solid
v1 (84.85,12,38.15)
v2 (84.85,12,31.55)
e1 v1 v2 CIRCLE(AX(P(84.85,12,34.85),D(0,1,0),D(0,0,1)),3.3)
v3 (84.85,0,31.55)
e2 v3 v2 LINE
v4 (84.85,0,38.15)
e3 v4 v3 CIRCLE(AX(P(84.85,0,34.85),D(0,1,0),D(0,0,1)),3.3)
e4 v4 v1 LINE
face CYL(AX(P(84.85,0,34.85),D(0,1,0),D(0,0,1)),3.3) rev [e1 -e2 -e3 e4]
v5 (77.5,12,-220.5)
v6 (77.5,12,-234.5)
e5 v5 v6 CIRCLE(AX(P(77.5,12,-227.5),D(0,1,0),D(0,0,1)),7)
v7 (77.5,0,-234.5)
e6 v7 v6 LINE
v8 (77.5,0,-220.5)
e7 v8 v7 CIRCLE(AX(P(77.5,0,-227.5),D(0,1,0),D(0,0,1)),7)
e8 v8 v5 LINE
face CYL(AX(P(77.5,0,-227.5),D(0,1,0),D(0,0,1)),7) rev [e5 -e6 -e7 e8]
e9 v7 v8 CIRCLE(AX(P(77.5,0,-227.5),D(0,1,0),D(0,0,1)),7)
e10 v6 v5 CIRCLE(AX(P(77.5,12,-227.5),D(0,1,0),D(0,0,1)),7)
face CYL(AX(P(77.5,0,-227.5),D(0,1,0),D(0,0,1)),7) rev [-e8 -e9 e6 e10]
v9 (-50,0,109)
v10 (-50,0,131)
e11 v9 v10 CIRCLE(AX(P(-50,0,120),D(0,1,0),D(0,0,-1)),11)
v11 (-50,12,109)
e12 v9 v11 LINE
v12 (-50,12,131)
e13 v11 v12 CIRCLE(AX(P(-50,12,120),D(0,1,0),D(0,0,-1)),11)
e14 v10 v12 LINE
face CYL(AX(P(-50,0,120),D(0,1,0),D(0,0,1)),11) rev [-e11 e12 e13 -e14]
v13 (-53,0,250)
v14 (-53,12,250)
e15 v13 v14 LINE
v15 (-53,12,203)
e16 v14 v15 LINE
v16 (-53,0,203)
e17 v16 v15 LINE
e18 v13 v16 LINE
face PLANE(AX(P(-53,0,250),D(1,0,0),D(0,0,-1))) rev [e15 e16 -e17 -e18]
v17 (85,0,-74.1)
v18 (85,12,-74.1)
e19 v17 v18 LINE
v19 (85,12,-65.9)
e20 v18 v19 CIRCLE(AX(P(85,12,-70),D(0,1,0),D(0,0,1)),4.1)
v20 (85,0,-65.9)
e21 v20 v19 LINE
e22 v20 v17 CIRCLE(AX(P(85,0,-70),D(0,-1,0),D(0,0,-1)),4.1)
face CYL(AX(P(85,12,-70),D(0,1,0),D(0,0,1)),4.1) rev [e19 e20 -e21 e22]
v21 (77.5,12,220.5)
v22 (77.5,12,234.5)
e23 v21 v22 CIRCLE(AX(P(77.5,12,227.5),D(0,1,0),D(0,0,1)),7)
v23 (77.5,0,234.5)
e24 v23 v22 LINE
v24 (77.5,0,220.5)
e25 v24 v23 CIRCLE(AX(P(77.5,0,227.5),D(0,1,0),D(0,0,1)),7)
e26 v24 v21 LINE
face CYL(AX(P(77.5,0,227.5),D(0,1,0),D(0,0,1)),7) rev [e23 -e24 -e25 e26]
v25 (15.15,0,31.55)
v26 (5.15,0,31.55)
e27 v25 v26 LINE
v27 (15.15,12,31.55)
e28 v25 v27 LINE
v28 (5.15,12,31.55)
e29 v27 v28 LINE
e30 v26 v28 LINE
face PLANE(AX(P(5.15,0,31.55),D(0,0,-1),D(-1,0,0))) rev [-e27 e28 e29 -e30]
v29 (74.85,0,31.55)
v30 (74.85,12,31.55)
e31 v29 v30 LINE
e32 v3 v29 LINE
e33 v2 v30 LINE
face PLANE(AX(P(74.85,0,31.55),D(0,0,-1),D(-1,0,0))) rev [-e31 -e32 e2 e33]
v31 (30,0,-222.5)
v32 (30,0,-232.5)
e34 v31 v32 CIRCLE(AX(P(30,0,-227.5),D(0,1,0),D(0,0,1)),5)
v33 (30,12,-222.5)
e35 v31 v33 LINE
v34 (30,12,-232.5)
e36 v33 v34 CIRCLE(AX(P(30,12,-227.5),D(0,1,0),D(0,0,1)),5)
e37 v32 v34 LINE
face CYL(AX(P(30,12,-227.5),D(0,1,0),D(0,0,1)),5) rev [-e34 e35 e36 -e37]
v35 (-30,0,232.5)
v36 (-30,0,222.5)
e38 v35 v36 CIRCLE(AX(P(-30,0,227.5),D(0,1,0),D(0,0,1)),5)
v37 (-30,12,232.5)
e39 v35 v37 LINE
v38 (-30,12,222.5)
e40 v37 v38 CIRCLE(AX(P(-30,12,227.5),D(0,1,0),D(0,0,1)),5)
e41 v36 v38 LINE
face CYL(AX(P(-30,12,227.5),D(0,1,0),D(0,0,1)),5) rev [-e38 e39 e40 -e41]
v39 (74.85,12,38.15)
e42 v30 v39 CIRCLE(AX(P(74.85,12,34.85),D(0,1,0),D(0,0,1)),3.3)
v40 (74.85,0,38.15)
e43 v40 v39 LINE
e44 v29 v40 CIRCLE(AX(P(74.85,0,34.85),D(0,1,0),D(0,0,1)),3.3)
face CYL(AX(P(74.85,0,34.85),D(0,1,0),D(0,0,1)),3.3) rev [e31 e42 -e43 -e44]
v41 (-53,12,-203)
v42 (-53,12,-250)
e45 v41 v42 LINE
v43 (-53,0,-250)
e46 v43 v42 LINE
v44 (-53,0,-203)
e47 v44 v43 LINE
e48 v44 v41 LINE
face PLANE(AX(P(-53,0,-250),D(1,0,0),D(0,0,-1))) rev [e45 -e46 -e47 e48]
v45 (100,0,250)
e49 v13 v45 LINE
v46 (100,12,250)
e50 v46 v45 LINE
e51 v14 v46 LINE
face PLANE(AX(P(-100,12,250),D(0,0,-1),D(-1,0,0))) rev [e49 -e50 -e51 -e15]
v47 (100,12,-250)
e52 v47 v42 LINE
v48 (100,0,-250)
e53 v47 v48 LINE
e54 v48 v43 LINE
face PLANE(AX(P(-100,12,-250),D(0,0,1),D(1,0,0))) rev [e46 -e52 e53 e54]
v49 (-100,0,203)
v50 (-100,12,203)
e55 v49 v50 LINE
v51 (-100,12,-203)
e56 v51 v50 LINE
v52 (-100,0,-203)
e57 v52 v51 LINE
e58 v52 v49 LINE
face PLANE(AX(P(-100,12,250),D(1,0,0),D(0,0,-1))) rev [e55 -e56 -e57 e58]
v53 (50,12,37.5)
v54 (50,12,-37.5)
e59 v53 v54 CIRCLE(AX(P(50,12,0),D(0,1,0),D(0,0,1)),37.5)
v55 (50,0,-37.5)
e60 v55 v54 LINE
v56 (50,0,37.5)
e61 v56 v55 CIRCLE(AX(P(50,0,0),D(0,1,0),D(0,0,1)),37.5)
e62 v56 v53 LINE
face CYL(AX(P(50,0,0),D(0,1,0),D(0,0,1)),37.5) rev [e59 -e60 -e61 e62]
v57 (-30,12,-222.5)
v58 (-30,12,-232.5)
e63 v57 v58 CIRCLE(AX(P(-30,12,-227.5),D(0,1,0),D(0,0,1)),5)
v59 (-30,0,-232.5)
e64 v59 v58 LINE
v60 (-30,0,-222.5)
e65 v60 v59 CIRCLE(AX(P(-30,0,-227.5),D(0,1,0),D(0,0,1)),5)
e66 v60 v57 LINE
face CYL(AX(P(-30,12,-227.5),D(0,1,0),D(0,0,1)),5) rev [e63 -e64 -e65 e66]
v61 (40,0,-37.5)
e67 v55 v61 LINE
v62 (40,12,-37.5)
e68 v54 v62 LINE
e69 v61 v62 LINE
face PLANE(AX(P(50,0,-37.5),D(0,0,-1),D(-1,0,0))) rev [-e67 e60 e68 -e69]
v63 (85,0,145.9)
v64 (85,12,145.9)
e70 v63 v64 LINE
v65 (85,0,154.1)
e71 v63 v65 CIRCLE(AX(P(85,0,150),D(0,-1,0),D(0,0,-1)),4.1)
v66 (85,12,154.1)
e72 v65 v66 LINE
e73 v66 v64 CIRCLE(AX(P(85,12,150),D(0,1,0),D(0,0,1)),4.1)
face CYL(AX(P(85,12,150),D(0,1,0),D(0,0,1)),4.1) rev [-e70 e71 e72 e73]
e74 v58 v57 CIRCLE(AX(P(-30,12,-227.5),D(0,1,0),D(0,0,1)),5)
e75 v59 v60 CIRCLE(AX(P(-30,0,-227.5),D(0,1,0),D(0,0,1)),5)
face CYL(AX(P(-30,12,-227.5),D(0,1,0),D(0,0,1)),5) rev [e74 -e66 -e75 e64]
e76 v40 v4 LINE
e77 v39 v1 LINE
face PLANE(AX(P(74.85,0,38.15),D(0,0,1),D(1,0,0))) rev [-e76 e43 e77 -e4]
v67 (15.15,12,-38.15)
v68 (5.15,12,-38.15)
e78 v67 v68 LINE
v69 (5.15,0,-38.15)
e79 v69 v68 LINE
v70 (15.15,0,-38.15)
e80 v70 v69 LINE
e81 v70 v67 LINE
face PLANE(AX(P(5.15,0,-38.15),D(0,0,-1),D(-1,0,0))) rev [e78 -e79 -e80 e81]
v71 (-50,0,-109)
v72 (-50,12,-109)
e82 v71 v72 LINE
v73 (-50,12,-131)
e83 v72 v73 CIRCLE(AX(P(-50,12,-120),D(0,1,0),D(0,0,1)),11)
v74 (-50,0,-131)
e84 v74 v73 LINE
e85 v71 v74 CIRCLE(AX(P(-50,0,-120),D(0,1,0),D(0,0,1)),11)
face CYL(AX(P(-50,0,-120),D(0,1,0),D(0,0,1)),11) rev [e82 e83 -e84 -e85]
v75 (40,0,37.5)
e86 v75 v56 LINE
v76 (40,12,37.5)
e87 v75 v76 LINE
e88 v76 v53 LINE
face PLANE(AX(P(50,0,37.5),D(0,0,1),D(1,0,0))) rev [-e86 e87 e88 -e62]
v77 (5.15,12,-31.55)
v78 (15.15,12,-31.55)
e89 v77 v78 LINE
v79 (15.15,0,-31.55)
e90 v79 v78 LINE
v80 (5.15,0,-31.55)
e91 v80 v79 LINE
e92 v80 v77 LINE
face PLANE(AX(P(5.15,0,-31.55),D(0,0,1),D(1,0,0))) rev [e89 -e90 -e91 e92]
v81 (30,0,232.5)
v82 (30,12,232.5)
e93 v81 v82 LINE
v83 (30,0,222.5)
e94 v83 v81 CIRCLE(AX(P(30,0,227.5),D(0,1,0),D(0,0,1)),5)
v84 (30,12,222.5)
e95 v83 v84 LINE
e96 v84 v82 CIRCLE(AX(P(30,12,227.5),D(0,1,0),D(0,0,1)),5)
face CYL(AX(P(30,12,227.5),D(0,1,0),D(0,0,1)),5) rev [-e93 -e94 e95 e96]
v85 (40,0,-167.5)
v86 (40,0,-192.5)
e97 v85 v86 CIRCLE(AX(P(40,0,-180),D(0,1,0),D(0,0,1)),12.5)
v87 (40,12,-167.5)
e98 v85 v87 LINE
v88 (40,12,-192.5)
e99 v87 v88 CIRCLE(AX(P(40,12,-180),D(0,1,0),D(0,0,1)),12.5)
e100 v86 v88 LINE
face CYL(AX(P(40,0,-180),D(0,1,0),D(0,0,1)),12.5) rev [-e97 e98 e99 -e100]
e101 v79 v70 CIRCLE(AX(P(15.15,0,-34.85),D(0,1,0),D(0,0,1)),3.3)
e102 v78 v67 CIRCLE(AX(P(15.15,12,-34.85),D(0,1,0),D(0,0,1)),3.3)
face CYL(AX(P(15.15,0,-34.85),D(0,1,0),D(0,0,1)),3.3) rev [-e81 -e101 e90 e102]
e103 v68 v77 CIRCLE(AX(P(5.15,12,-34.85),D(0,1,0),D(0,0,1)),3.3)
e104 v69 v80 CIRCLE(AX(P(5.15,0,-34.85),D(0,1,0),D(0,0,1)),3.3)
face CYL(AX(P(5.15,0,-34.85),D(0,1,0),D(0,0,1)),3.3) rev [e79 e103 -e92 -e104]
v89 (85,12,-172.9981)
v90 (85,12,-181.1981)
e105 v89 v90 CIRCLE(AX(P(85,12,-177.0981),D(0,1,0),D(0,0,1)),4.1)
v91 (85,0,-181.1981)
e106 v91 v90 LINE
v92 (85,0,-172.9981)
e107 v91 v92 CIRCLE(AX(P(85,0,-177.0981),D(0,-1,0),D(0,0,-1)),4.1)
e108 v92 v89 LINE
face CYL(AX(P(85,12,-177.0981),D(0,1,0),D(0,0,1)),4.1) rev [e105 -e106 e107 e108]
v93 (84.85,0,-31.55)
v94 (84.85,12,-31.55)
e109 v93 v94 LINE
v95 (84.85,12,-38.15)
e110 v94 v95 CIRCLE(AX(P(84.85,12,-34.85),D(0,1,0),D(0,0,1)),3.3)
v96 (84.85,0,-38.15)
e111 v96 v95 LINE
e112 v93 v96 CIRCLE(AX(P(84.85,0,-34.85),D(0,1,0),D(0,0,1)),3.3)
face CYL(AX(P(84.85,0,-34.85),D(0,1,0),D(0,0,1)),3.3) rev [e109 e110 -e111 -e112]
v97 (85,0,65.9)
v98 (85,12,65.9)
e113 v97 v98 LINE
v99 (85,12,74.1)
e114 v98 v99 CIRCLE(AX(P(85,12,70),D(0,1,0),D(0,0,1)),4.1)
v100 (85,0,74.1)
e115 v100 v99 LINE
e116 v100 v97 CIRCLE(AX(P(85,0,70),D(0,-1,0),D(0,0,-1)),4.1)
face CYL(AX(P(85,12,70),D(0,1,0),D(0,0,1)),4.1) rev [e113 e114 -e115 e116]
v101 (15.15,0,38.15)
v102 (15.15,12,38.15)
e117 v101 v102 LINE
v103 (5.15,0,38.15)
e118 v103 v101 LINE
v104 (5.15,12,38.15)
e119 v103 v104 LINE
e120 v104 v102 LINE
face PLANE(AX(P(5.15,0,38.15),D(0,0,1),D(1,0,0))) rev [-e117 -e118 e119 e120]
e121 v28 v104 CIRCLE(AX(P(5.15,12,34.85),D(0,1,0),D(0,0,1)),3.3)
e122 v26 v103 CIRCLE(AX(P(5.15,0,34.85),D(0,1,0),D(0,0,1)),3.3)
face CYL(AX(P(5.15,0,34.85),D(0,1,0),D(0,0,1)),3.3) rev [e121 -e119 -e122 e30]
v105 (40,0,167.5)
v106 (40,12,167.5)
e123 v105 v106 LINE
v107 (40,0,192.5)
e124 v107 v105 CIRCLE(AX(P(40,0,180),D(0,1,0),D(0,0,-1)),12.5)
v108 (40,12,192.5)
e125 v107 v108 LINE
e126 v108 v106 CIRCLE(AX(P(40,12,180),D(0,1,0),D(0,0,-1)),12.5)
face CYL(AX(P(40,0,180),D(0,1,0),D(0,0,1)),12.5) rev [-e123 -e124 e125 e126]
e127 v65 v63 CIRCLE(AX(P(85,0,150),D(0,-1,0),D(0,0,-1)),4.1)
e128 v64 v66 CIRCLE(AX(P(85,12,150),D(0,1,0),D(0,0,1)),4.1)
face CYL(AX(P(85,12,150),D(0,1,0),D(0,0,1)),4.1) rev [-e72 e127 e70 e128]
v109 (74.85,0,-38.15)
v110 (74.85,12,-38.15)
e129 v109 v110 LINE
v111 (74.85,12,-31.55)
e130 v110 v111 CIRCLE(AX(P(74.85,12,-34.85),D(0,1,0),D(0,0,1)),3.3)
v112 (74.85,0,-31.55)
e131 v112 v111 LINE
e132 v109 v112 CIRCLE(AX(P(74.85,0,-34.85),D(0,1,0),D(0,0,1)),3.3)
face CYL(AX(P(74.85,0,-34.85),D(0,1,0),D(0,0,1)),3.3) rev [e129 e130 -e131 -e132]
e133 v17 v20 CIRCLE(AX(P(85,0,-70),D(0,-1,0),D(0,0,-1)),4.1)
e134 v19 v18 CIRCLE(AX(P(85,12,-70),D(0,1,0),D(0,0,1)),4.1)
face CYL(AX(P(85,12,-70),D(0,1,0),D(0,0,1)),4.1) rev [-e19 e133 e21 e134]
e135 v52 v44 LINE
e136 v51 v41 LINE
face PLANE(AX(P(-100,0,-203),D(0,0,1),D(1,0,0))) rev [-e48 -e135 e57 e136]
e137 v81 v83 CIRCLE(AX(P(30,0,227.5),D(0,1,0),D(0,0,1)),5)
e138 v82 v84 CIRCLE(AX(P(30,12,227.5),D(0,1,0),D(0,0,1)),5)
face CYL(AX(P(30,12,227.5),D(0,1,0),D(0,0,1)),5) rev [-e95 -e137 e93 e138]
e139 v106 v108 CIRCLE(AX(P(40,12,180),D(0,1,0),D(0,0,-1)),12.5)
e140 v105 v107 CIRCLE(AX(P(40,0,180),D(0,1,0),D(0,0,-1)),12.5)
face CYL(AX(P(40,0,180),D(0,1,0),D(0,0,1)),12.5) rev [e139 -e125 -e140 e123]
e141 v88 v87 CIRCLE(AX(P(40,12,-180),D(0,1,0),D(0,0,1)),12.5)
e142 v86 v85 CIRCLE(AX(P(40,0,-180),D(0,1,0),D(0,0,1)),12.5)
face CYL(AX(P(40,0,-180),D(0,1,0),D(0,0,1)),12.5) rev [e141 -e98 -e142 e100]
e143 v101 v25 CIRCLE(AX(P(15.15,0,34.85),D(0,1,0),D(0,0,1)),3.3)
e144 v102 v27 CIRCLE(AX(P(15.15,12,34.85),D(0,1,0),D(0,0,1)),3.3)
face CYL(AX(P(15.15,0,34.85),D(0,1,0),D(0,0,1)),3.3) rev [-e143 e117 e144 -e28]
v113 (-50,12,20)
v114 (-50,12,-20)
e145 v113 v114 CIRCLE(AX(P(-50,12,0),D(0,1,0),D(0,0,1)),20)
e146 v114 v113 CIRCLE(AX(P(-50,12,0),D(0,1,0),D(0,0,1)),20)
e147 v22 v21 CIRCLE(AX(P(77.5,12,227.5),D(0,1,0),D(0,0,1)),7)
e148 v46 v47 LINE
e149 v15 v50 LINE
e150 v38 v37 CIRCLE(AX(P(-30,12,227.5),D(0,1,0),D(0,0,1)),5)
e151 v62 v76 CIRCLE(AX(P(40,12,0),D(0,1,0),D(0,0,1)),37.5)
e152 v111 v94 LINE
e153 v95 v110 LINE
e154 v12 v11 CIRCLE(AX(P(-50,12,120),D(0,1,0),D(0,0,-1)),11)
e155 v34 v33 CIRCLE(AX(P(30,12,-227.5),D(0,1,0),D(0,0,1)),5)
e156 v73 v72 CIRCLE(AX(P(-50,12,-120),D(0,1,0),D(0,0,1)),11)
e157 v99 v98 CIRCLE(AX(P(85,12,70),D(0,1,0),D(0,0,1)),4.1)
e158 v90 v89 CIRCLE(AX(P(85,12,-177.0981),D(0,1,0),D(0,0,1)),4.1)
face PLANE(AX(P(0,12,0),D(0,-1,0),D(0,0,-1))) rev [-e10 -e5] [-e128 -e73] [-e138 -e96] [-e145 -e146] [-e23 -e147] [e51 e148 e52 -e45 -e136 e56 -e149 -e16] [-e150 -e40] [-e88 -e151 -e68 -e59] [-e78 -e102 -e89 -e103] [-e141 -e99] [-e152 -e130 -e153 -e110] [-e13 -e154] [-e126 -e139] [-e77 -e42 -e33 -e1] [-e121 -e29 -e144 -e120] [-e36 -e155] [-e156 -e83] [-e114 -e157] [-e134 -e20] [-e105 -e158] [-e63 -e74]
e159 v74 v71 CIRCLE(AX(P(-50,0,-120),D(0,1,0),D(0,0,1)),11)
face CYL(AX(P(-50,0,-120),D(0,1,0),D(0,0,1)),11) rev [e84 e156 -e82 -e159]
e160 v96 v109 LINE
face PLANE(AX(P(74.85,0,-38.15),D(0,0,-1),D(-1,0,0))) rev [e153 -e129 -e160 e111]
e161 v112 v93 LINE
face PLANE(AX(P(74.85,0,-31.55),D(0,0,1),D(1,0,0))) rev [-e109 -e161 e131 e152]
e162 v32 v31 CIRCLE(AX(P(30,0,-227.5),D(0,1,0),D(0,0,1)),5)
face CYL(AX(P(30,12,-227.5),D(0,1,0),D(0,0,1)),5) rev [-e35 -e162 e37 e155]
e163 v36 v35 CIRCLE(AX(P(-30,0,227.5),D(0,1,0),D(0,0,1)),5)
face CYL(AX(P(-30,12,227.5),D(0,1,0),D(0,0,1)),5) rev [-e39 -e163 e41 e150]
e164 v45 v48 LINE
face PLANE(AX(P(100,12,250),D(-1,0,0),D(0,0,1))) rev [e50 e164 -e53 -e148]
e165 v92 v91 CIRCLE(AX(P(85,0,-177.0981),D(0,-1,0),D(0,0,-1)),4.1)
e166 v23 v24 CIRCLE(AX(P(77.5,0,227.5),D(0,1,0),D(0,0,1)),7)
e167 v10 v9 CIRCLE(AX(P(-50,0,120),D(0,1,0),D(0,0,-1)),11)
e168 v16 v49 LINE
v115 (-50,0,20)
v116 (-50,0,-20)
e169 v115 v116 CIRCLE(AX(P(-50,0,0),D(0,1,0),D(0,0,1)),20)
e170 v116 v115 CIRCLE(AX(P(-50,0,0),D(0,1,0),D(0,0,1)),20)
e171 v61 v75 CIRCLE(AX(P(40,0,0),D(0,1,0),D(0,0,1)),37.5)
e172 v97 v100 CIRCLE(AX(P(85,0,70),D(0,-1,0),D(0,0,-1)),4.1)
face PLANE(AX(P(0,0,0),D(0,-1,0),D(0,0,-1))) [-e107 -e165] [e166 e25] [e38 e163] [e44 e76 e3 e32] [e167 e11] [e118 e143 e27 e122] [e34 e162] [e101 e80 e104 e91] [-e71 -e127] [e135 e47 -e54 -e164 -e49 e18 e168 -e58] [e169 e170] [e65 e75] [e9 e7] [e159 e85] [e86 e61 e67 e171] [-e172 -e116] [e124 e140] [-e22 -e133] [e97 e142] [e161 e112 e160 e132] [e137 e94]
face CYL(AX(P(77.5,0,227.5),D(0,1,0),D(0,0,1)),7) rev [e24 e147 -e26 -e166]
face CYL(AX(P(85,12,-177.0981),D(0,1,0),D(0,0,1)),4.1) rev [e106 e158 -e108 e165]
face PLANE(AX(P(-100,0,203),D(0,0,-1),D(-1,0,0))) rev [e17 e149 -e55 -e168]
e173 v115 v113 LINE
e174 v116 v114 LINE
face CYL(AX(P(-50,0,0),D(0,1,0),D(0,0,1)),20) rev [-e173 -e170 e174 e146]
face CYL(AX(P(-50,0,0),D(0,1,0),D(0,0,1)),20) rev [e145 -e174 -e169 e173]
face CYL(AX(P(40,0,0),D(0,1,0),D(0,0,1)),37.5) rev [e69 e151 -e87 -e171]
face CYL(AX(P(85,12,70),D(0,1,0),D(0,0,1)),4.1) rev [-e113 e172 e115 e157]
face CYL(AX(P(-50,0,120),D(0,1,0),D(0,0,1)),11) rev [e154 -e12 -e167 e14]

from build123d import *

# Parameters (mm, degrees)
SKETCH1_W                      = 200
SKETCH1_H                      = 500
BOSS_EXTRUDE1_DEPTH            = 12
SKETCH2_R                      = 20
SKETCH2_R_2                    = 11
CUT_EXTRUDE1_DEPTH             = 12
SKETCH4_R                      = 12.5
CUT_EXTRUDE3_DEPTH             = 12
SKETCH5_R                      = 7
CUT_EXTRUDE4_DEPTH             = 12
F_8_2_8_2_DIAMETER_HOLE1_D     = 8.2
F_8_2_8_2_DIAMETER_HOLE1_DEPTH = 13
F_8_2_8_2_DIAMETER_HOLE1_TIP   = 2.463528538
F_10_0_10_DIAMETER_HOLE1_D     = 10
SKETCH11_W                     = 47
SKETCH11_H                     = 47
CUT_EXTRUDE6_DEPTH             = 270.525508997
CUT_EXTRUDE7_DEPTH             = 270.525508997
F_5_0_5_DIAMETER_HOLE1_D       = 5
CUT_EXTRUDE8_DEPTH             = 270.525508997


with BuildPart() as part:
    # Sketch1 → Boss-Extrude1 (new body)
    with BuildSketch(Plane(origin=(0, 0, 0), x_dir=(1, 0, 0), z_dir=(0, 1, 0))):
        Rectangle(SKETCH1_W, SKETCH1_H)
    extrude(amount=BOSS_EXTRUDE1_DEPTH)

    # Sketch2 → Cut-Extrude1 (cut)
    with BuildSketch(Plane(origin=(0, 12, 0), x_dir=(1, 0, 0), z_dir=(0, 1, 0))):
        with Locations(Location((-50, 0, 0), (0, 0, 270))):
            Circle(SKETCH2_R)
        with Locations(Location((-50, 120, 0), (0, 0, 270))):
            Circle(SKETCH2_R_2)
        with Locations(Location((-50, -120, 0), (0, 0, 90))):
            Circle(SKETCH2_R_2)
    extrude(amount=-CUT_EXTRUDE1_DEPTH, mode=Mode.SUBTRACT)

    # Sketch4 → Cut-Extrude3 (cut)
    with BuildSketch(Plane(origin=(0, 12, 0), x_dir=(1, 0, 0), z_dir=(0, 1, 0))):
        with Locations(Location((40, 180, 0), (0, 0, 270))):
            Circle(SKETCH4_R)
        with Locations(Location((40, -180, 0), (0, 0, 90))):
            Circle(SKETCH4_R)
    extrude(amount=-CUT_EXTRUDE3_DEPTH, mode=Mode.SUBTRACT)

    # Sketch5 → Cut-Extrude4 (cut)
    with BuildSketch(Plane(origin=(0, 12, 0), x_dir=(1, 0, 0), z_dir=(0, 1, 0))):
        with Locations(Location((-77.5, 227.5, 0), (0, 0, 270))):
            Circle(SKETCH5_R)
        with Locations(Location((77.5, 227.5, 0), (0, 0, 270))):
            Circle(SKETCH5_R)
        with Locations(Location((-77.5, -227.5, 0), (0, 0, 270))):
            Circle(SKETCH5_R)
        with Locations(Location((77.5, -227.5, 0), (0, 0, 270))):
            Circle(SKETCH5_R)
    extrude(amount=-CUT_EXTRUDE4_DEPTH, mode=Mode.SUBTRACT)

    # Ø8.2 (8.2) Diameter Hole1
    with Locations(Plane(origin=(0, 12, 0), x_dir=(1, 0, 0), z_dir=(0, 1, 0))):
        with Locations((85, 177.098099642), (85, 70), (85, -70), (85, -150)):
            Hole(F_8_2_8_2_DIAMETER_HOLE1_D / 2, depth=F_8_2_8_2_DIAMETER_HOLE1_DEPTH)
            with Locations((0, 0, -(F_8_2_8_2_DIAMETER_HOLE1_DEPTH + F_8_2_8_2_DIAMETER_HOLE1_TIP / 2))):  # 118° drill point
                Cone(0, F_8_2_8_2_DIAMETER_HOLE1_D / 2, F_8_2_8_2_DIAMETER_HOLE1_TIP, mode=Mode.SUBTRACT)

    # Ø10.0 (10) Diameter Hole1 (through all)
    with Locations(Plane(origin=(0, 12, 0), x_dir=(1, 0, 0), z_dir=(0, 1, 0))):
        with Locations((-30, 227.5), (30, 227.5), (30, -227.5), (-30, -227.5)):
            Hole(F_10_0_10_DIAMETER_HOLE1_D / 2)

    # Sketch11 → Cut-Extrude6 (cut, through all)
    with BuildSketch(Plane(origin=(0, 12, 0), x_dir=(1, 0, 0), z_dir=(0, 1, 0))):
        with Locations((-76.5, 226.5)):
            Rectangle(SKETCH11_W, SKETCH11_H)
        with Locations((-76.5, -226.5)):
            Rectangle(SKETCH11_W, SKETCH11_H)
    extrude(amount=-CUT_EXTRUDE6_DEPTH, mode=Mode.SUBTRACT)

    # Sketch3 → Cut-Extrude7 (cut, through all)
    with BuildSketch(Plane(origin=(0, 12, 0), x_dir=(1, 0, 0), z_dir=(0, 1, 0))):
        with BuildLine():
            Line((50, -37.5), (40, -37.5))
            ThreePointArc((40, -37.5), (2.5, 0), (40, 37.5))
            Line((40, 37.5), (50, 37.5))
            ThreePointArc((50, 37.5), (87.5, 0), (50, -37.5))
        make_face()
    extrude(amount=-CUT_EXTRUDE7_DEPTH, mode=Mode.SUBTRACT)

    # Ø5.0 (5) Diameter Hole1 (through all)
    with Locations(Plane(origin=(0, 12, 0), x_dir=(1, 0, 0), z_dir=(0, 1, 0))):
        with Locations((5.15, 34.85), (5.15, -34.85), (74.85, -34.85), (74.85, 34.85)):
            Hole(F_5_0_5_DIAMETER_HOLE1_D / 2)

    # Sketch16 → Cut-Extrude8 (cut, through all)
    with BuildSketch(Plane(origin=(0, 12, 0), x_dir=(1, 0, 0), z_dir=(0, 1, 0))):
        with BuildLine():
            Line((5.15, 38.15), (15.15, 38.15))
            ThreePointArc((15.15, 38.15), (18.45, 34.85), (15.15, 31.55))
            Line((15.15, 31.55), (5.15, 31.55))
            ThreePointArc((5.15, 31.55), (1.85, 34.85), (5.15, 38.15))
        make_face()
        with BuildLine():
            Line((74.85, 38.15), (84.85, 38.15))
            ThreePointArc((84.85, 38.15), (88.15, 34.85), (84.85, 31.55))
            Line((84.85, 31.55), (74.85, 31.55))
            ThreePointArc((74.85, 31.55), (71.55, 34.85), (74.85, 38.15))
        make_face()
        with BuildLine():
            Line((5.15, -31.55), (15.15, -31.55))
            ThreePointArc((15.15, -31.55), (18.45, -34.85), (15.15, -38.15))
            Line((15.15, -38.15), (5.15, -38.15))
            ThreePointArc((5.15, -38.15), (1.85, -34.85), (5.15, -31.55))
        make_face()
        with BuildLine():
            Line((74.85, -31.55), (84.85, -31.55))
            ThreePointArc((84.85, -31.55), (88.15, -34.85), (84.85, -38.15))
            Line((84.85, -38.15), (74.85, -38.15))
            ThreePointArc((74.85, -38.15), (71.55, -34.85), (74.85, -31.55))
        make_face()
    extrude(amount=-CUT_EXTRUDE8_DEPTH, mode=Mode.SUBTRACT)


solid = part.part
